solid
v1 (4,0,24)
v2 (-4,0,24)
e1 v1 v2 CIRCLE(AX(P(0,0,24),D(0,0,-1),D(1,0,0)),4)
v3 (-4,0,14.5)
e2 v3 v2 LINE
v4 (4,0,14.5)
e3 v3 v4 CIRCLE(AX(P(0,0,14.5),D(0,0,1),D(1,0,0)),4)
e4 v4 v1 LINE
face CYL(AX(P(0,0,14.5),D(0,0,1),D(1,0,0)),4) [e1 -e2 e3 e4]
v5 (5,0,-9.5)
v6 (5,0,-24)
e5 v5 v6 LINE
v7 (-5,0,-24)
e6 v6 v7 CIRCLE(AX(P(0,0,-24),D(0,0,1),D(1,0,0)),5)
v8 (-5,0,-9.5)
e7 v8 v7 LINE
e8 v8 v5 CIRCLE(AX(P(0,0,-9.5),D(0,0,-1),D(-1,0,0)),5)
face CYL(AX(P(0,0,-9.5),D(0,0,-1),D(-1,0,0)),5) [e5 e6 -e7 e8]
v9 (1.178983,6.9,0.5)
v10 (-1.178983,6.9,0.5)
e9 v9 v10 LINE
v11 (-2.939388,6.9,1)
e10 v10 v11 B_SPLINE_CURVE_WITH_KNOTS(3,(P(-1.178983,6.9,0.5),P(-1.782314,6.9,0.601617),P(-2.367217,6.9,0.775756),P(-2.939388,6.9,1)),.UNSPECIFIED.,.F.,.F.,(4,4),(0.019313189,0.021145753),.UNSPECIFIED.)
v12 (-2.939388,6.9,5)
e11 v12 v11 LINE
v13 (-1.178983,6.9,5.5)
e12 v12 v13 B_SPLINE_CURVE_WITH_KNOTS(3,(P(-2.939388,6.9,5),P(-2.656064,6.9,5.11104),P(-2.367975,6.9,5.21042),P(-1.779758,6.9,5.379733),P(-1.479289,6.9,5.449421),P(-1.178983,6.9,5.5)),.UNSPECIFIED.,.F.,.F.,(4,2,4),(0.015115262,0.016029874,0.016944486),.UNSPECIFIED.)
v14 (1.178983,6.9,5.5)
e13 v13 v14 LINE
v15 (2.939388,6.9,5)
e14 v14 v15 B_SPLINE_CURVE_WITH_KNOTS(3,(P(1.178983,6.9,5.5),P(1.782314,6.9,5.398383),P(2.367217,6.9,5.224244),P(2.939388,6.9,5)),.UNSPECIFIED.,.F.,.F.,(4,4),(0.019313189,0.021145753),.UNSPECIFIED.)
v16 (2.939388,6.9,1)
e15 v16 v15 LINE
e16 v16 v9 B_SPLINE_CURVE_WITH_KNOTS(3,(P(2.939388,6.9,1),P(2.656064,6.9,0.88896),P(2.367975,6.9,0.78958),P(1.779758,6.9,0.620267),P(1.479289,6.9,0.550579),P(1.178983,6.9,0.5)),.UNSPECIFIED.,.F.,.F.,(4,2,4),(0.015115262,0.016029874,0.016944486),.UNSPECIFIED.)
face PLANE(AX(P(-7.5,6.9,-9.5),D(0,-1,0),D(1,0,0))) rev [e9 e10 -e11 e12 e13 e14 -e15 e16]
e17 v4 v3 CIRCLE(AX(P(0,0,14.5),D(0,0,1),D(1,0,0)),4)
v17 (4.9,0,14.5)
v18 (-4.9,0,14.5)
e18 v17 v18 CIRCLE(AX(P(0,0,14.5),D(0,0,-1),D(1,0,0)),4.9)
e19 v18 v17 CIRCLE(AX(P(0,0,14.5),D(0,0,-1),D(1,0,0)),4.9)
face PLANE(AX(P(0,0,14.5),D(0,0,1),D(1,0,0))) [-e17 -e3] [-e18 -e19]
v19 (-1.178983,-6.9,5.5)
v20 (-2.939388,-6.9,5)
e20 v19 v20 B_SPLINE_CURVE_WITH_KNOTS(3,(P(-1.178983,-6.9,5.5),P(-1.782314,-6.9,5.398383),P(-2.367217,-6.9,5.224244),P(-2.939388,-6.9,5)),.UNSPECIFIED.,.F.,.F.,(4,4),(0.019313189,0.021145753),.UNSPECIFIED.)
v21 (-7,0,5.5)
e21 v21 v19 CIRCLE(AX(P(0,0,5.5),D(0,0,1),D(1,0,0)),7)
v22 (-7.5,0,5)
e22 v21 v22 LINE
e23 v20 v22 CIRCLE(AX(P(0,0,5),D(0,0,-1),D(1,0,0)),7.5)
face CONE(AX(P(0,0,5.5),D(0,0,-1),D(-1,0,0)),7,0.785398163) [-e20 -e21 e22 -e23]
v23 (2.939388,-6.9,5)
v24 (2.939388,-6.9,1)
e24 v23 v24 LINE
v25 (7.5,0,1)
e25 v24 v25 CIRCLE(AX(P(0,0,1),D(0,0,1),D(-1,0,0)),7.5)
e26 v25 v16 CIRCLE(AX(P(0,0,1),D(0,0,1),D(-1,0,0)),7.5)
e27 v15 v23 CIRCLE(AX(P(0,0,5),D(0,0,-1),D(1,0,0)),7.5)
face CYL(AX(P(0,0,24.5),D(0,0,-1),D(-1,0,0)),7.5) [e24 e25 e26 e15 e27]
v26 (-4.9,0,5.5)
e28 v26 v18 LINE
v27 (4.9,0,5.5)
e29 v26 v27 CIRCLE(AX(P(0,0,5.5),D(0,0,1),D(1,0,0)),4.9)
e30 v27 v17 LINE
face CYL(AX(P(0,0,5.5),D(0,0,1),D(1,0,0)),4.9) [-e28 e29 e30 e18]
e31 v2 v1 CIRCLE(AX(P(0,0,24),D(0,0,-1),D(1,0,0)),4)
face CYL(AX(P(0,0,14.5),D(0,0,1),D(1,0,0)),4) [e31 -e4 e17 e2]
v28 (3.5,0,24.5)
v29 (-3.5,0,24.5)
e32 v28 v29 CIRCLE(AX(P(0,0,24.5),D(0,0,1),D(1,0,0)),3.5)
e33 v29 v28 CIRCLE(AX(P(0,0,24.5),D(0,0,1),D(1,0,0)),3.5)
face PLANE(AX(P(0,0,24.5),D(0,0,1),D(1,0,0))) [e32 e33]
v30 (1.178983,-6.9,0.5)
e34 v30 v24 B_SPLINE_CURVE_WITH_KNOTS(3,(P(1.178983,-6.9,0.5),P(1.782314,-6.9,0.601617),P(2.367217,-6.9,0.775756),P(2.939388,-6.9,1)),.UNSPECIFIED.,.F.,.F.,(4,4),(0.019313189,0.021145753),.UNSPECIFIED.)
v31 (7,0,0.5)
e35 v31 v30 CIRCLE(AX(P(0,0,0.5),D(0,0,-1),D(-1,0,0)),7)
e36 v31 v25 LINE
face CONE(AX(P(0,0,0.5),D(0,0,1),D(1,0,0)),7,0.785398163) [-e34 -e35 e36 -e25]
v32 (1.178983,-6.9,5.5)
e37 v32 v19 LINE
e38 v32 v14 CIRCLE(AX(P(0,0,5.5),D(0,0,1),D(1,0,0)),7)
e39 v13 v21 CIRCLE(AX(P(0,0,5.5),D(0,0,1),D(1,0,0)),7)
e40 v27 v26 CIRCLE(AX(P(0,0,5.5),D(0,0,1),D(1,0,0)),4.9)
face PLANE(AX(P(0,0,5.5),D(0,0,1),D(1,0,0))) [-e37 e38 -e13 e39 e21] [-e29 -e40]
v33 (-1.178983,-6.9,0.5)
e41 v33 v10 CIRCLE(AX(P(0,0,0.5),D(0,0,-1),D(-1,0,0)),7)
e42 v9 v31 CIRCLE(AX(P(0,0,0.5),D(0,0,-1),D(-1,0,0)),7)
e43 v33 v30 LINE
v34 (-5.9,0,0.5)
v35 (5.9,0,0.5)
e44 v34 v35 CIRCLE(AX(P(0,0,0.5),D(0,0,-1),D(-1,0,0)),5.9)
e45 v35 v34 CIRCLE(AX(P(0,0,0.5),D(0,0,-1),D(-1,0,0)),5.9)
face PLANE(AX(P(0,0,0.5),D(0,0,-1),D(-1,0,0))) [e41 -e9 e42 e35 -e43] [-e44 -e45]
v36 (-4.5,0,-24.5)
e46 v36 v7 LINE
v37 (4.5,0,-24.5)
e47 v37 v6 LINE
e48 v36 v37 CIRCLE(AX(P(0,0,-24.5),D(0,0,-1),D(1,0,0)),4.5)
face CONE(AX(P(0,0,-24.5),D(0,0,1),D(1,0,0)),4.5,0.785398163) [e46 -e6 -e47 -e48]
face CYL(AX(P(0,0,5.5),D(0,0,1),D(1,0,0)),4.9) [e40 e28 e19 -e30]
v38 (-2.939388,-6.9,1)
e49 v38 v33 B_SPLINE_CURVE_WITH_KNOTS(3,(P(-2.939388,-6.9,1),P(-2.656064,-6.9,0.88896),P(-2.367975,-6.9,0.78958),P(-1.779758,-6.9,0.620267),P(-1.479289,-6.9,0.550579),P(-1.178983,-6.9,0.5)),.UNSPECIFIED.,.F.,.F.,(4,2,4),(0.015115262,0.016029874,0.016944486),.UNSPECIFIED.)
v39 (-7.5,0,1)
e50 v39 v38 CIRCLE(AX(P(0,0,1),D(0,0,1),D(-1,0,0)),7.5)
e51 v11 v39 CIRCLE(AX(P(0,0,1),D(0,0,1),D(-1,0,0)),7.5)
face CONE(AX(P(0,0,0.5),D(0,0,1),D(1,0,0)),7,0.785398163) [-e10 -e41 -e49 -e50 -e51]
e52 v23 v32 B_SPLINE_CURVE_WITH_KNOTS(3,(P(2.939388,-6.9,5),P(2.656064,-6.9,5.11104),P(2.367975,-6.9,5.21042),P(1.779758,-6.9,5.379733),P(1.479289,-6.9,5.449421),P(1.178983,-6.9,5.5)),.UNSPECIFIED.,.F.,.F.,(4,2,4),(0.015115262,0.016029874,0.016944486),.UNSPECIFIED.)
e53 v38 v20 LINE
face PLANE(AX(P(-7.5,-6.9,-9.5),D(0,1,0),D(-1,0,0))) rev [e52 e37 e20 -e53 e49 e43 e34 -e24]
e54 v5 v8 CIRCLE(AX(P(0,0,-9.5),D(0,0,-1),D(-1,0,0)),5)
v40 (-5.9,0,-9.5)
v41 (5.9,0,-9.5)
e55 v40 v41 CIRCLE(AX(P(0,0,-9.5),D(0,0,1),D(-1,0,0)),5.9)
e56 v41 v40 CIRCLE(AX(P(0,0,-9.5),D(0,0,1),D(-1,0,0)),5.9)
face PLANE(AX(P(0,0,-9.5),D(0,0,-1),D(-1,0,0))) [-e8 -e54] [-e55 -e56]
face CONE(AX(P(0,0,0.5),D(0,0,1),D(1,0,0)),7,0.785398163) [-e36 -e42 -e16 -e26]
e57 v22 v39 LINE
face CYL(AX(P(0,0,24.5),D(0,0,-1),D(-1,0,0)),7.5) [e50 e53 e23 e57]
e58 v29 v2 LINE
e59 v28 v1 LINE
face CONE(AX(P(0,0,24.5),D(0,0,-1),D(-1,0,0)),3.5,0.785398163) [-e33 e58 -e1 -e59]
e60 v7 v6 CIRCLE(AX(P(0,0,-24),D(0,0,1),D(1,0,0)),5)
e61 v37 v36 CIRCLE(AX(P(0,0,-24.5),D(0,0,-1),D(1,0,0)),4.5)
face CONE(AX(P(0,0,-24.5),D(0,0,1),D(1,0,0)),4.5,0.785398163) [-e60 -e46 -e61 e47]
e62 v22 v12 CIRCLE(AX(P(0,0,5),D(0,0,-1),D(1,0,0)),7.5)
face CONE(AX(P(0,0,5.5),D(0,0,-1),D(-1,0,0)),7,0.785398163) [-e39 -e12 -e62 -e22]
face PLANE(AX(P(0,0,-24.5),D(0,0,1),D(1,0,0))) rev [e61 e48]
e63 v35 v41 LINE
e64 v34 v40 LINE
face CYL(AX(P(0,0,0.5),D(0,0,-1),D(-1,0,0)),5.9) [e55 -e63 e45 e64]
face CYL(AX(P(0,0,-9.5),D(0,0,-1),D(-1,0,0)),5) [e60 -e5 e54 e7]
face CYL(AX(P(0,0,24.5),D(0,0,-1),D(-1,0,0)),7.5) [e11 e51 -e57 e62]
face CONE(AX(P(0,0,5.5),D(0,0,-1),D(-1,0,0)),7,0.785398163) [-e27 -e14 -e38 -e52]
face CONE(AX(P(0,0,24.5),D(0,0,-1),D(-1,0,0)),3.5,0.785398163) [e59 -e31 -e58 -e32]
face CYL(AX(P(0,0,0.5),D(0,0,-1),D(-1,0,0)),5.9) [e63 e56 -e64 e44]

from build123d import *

# Parameters (mm, degrees)
SKETCH_1_R          = 7.5
EXTRUDE_1_DEPTH     = 24.5
SKETCH_2_OUTSIDE_W  = 27.678
SKETCH_2_OUTSIDE_H  = 27.678
SKETCH_2_OUTSIDE_R  = 4.9
CUT_EXTRUDE_1_DEPTH = 19
SKETCH_3_OUTSIDE_W  = 27.678
SKETCH_3_OUTSIDE_H  = 27.678
SKETCH_3_OUTSIDE_R  = 4
CUT_EXTRUDE_2_DEPTH = 10
SKETCH_4_OUTSIDE_W  = 27.678
SKETCH_4_OUTSIDE_H  = 27.678
SKETCH_4_OUTSIDE_R  = 5.9
CUT_EXTRUDE_3_DEPTH = 25
SKETCH_5_OUTSIDE_W  = 27.678
SKETCH_5_OUTSIDE_H  = 27.678
SKETCH_5_OUTSIDE_R  = 5
CUT_EXTRUDE_4_DEPTH = 15
CHAMFER_1_SIZE      = 0.5
SKETCH_6_W          = 15
SKETCH_6_H          = 6
CUT_EXTRUDE_5_DEPTH = 15


with BuildPart() as part:
    # 草图1 → 凸台-拉伸1 (new, symmetric)
    with BuildSketch(Plane.XY):
        Circle(SKETCH_1_R)
    extrude(amount=EXTRUDE_1_DEPTH, both=True)

    # 草图2 outside → 切除-拉伸1 (cut)
    with BuildSketch(Plane.XY.offset(24.5)):
        Rectangle(SKETCH_2_OUTSIDE_W, SKETCH_2_OUTSIDE_H)
        Circle(SKETCH_2_OUTSIDE_R, mode=Mode.SUBTRACT)
    extrude(amount=-CUT_EXTRUDE_1_DEPTH, mode=Mode.SUBTRACT)

    # 草图3 outside → 切除-拉伸2 (cut)
    with BuildSketch(Plane.XY.offset(24.5)):
        Rectangle(SKETCH_3_OUTSIDE_W, SKETCH_3_OUTSIDE_H)
        Circle(SKETCH_3_OUTSIDE_R, mode=Mode.SUBTRACT)
    extrude(amount=-CUT_EXTRUDE_2_DEPTH, mode=Mode.SUBTRACT)

    # 草图4 outside → 切除-拉伸3 (cut)
    with BuildSketch(Plane(origin=(0, 0, -24.5), x_dir=(-1, 0, 0), z_dir=(0, 0, -1))):
        Rectangle(SKETCH_4_OUTSIDE_W, SKETCH_4_OUTSIDE_H)
        Circle(SKETCH_4_OUTSIDE_R, mode=Mode.SUBTRACT)
    extrude(amount=-CUT_EXTRUDE_3_DEPTH, mode=Mode.SUBTRACT)

    # 草图5 outside → 切除-拉伸4 (cut)
    with BuildSketch(Plane(origin=(0, 0, -24.5), x_dir=(-1, 0, 0), z_dir=(0, 0, -1))):
        Rectangle(SKETCH_5_OUTSIDE_W, SKETCH_5_OUTSIDE_H)
        Circle(SKETCH_5_OUTSIDE_R, mode=Mode.SUBTRACT)
    extrude(amount=-CUT_EXTRUDE_4_DEPTH, mode=Mode.SUBTRACT)

    # 倒角1
    chamfer_1_edges = [part.edges().sort_by_distance(p)[0] for p in [
        (-4, 0, 24.5),
        (-7.5, 0, 0.5),
        (5, 0, -24.5),
        (-7.5, 0, 5.5),
    ]]
    chamfer(chamfer_1_edges, length=CHAMFER_1_SIZE)

    # 草图6 → 切除-拉伸5 (cut)
    with BuildSketch(Plane.XY.offset(5.5)):
        with Locations((0, 9.9)):
            Rectangle(SKETCH_6_W, SKETCH_6_H)
        with Locations((0, -9.9)):
            Rectangle(SKETCH_6_W, SKETCH_6_H)
    extrude(amount=-CUT_EXTRUDE_5_DEPTH, mode=Mode.SUBTRACT)


solid = part.part
